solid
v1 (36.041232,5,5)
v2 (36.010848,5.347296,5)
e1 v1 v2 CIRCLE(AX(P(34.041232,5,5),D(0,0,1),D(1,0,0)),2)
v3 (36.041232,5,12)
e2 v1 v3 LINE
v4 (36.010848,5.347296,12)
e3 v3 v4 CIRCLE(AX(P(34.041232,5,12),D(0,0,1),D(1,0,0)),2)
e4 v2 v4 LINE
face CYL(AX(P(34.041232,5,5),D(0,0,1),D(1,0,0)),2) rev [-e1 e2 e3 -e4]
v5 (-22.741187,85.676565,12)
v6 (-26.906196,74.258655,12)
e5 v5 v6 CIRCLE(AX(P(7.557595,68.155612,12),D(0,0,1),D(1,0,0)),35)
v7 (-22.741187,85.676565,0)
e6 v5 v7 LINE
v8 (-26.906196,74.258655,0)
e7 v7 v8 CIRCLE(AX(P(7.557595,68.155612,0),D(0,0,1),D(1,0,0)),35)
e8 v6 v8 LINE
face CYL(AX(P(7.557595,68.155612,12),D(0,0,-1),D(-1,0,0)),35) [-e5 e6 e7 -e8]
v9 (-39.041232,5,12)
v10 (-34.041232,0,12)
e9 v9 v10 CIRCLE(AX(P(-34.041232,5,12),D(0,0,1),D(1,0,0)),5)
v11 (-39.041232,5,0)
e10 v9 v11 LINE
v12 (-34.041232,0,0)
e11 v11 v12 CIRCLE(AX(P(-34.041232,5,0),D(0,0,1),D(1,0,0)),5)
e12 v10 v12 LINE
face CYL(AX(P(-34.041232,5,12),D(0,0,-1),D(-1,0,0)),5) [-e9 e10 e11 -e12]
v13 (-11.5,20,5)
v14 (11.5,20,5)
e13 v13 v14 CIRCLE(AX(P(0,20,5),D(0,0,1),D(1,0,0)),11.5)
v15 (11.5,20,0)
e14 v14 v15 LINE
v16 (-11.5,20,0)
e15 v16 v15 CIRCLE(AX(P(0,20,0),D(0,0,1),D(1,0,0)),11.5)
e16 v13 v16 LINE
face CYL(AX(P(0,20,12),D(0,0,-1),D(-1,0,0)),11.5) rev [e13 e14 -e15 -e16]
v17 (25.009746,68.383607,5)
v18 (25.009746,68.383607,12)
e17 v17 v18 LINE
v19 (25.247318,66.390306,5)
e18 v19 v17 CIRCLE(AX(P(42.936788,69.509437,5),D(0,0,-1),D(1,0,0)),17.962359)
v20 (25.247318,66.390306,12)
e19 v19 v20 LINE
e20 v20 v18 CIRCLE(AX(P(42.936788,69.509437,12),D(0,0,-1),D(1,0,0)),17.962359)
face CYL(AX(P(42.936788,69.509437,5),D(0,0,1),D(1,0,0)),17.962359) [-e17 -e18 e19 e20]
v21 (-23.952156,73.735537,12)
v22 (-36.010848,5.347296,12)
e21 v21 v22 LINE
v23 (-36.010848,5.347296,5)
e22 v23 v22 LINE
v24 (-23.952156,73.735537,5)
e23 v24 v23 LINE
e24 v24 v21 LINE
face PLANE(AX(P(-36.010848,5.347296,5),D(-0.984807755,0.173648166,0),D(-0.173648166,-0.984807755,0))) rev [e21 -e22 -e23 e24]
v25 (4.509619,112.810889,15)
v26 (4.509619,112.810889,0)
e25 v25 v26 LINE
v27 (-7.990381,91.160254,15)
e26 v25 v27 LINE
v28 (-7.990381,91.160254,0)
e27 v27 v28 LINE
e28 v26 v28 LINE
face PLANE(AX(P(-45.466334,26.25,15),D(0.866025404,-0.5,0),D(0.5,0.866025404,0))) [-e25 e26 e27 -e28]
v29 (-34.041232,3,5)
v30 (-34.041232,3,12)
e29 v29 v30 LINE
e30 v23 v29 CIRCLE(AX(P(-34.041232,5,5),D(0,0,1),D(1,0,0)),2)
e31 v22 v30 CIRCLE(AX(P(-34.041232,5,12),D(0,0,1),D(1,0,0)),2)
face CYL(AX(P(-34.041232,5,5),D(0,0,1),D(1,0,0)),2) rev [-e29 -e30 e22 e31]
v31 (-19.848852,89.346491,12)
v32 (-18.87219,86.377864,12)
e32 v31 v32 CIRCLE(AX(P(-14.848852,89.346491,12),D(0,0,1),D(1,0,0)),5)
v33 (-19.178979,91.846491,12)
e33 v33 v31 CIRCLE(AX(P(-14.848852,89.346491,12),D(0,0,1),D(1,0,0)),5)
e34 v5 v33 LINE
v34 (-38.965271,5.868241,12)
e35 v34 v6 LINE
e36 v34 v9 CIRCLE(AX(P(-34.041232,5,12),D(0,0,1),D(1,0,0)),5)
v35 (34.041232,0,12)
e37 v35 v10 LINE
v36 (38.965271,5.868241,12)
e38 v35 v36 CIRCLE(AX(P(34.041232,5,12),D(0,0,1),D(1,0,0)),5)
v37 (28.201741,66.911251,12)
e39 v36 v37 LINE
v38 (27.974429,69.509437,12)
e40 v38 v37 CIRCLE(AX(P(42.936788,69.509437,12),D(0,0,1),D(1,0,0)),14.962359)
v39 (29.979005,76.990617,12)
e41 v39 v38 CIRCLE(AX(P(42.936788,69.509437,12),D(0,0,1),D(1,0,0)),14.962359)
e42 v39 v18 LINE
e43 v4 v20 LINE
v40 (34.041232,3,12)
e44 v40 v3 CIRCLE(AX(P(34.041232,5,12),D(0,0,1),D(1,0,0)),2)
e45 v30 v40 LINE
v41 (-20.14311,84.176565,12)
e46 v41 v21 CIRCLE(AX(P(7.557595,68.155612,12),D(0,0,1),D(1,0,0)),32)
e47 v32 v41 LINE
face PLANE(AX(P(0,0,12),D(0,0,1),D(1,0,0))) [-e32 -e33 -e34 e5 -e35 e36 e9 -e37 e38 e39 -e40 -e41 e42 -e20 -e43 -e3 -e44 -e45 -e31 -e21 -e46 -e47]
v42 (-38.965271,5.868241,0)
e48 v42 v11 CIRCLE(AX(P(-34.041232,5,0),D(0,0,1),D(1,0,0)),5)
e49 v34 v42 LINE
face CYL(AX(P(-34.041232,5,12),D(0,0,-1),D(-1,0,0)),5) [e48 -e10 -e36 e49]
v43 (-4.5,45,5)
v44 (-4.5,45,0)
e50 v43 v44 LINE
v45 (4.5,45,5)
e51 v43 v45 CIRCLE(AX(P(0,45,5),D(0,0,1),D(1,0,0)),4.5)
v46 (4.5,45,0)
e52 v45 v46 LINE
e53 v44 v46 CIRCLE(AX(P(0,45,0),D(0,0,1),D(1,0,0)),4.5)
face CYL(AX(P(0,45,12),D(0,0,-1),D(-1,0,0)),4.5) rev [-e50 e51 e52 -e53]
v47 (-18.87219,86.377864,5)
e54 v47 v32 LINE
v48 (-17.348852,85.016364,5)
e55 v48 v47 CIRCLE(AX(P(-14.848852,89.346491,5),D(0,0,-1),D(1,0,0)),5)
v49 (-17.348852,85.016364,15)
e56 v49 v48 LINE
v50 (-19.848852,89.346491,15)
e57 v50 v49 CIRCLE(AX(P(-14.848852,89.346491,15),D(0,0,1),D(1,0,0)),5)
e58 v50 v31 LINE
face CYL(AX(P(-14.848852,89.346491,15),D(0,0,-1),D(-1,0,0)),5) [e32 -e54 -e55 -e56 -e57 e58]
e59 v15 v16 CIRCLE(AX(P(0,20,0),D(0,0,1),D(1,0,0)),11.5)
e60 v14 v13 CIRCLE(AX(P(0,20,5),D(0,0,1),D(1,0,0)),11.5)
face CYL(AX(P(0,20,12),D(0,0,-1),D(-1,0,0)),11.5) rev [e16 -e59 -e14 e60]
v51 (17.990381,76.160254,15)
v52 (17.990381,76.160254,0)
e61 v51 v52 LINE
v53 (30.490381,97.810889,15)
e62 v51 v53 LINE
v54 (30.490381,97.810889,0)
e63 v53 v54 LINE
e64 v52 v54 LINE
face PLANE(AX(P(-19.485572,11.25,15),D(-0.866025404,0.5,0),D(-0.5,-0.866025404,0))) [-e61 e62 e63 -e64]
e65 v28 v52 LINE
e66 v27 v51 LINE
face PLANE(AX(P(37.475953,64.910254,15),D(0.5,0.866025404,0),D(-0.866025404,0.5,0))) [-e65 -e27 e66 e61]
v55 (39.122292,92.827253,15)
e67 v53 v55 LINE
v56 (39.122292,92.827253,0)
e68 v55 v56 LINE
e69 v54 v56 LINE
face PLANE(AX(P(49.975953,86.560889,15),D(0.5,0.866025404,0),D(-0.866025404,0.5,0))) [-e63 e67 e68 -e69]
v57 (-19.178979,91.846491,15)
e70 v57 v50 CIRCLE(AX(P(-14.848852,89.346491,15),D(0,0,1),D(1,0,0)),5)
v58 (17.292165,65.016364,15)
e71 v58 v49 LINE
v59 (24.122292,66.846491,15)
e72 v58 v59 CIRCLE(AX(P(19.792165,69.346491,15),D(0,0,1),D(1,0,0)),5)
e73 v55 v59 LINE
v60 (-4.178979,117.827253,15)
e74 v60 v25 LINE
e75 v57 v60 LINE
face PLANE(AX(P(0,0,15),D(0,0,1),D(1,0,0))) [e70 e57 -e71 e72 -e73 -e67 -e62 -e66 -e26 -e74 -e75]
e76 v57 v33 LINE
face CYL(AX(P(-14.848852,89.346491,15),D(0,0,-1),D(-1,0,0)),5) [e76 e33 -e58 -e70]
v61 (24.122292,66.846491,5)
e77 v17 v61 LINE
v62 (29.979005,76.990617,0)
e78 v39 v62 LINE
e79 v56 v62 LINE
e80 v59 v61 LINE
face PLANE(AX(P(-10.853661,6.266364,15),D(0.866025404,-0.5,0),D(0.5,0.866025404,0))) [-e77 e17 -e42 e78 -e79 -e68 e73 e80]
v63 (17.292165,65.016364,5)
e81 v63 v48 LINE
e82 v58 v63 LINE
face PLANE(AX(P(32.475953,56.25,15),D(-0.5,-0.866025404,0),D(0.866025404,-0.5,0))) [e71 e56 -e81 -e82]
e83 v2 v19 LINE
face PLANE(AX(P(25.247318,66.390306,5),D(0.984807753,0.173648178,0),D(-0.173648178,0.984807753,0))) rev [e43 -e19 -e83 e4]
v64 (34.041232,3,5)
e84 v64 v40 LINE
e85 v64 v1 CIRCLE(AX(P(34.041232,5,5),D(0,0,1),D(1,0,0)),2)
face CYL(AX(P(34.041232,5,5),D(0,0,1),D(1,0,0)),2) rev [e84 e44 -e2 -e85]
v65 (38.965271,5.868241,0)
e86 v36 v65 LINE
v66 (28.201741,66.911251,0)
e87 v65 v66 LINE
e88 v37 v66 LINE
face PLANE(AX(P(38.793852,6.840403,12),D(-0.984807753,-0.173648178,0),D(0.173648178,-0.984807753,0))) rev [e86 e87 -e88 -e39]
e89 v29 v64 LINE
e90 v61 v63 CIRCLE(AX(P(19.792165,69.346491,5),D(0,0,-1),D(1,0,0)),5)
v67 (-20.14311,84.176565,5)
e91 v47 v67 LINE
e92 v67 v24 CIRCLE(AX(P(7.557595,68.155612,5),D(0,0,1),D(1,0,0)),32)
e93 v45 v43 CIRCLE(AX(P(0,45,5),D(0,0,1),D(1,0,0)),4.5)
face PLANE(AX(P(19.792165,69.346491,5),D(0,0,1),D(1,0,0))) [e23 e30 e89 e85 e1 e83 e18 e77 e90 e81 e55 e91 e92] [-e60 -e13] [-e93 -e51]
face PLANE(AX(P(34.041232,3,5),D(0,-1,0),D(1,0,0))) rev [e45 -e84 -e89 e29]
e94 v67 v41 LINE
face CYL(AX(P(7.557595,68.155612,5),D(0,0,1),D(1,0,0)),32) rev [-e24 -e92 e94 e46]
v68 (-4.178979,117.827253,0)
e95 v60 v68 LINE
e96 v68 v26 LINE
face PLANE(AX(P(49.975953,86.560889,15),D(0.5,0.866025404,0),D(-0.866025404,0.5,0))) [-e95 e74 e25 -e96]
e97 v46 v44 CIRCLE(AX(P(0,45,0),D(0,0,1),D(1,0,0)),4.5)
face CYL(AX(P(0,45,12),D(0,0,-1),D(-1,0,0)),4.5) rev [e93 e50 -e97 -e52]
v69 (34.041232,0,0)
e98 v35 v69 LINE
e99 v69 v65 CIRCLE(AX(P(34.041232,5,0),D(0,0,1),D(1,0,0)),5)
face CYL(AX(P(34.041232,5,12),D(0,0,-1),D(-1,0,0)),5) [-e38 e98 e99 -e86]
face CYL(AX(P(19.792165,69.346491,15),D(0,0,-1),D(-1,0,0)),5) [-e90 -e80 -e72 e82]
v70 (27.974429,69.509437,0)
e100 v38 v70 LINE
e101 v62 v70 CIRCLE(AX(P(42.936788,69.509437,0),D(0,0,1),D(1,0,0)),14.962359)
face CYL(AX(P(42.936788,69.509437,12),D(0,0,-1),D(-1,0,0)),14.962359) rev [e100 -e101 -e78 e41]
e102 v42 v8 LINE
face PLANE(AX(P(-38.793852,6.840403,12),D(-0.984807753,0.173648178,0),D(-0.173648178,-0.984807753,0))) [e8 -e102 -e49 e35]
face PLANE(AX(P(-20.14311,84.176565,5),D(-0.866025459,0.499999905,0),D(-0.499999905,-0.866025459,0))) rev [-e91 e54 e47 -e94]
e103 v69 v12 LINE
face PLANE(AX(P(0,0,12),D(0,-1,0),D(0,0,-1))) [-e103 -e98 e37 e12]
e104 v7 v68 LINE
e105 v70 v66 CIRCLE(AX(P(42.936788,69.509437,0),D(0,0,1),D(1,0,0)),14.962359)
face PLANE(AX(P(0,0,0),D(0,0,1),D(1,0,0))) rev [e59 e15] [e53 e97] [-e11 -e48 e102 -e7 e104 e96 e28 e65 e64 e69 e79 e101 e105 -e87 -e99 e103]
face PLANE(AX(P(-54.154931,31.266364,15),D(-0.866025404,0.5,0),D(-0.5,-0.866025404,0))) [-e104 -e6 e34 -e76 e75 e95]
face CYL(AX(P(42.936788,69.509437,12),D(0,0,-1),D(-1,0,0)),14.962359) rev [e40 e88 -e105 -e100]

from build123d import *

# Parameters (mm, degrees)
FORK_BOSS_15MM_DEPTH           = 15
SKETCH1_10_R                   = 11.5
SKETCH1_10_R_2                 = 4.5
PLATE_BOSS_12MM_DEPTH          = 12
POCKET_START                   = -7
POCKET_AND_HOLES_CUT_7MM_DEPTH = 7


with BuildPart() as part:
    # Bracket Outline Sketch → Fork Boss 15mm (new body)
    with BuildSketch(Plane.XY):
        with BuildLine():
            Line((-17.348851567, 85.016364122), (17.292164585, 65.016364122))
            ThreePointArc((17.292164585, 65.016364122), (21.08625981, 64.51686201), (24.122291604, 66.846491141))
            Line((24.122291604, 66.846491141), (29.979005279, 76.990616791))
            Line((29.979005279, 76.990616791), (39.122291604, 92.827253255))
            Line((39.122291604, 92.827253255), (30.490381057, 97.810889132))
            Line((30.490381057, 97.810889132), (17.990381057, 76.160254038))
            Line((17.990381057, 76.160254038), (-7.990381057, 91.160254038))
            Line((-7.990381057, 91.160254038), (4.509618943, 112.810889132))
            Line((4.509618943, 112.810889132), (-4.178978585, 117.827253255))
            Line((-4.178978585, 117.827253255), (-19.178978585, 91.846491141))
            ThreePointArc((-19.178978585, 91.846491141), (-19.678480698, 88.052395915), (-17.348851567, 85.016364122))
        make_face()
    extrude(amount=FORK_BOSS_15MM_DEPTH)

    # Sketch1_10 → Plate Boss 12mm (add)
    with BuildSketch(Plane.XY):
        with BuildLine():
            ThreePointArc((24.122291604, 66.846491141), (21.08625981, 64.51686201), (17.292164585, 65.016364122))
            Line((17.292164585, 65.016364122), (-17.348851567, 85.016364122))
            ThreePointArc((-17.348851567, 85.016364122), (-19.678480698, 88.052395915), (-19.178978585, 91.846491141))
            Line((-19.178978585, 91.846491141), (-22.741186866, 85.676565412))
            ThreePointArc((-22.741186866, 85.676565412), (-25.323096431, 80.149782404), (-26.906195607, 74.258654802))
            Line((-26.906195607, 74.258654802), (-38.965270802, 5.868240888))
            ThreePointArc((-38.965270802, 5.868240888), (-37.871454253, 1.786061952), (-34.041232037, 0))
            Line((-34.041232037, 0), (34.041232037, 0))
            ThreePointArc((34.041232037, 0), (37.871454253, 1.786061952), (38.965270802, 5.868240888))
            Line((38.965270802, 5.868240888), (28.201741138, 66.911250985))
            ThreePointArc((28.201741138, 66.911250985), (28.201741138, 72.107623698), (29.979005279, 76.990616791))
            Line((29.979005279, 76.990616791), (24.122291604, 66.846491141))
        make_face()
        with Locations((0, 20)):
            Circle(SKETCH1_10_R, mode=Mode.SUBTRACT)
        with Locations((0, 45)):
            Circle(SKETCH1_10_R_2, mode=Mode.SUBTRACT)
    extrude(amount=PLATE_BOSS_12MM_DEPTH)

    # Pocket and Holes Sketch → Pocket and Holes Cut 7mm (cut)
    with BuildSketch(Plane.XY.offset(12).offset(POCKET_START)):
        with BuildLine():
            Line((25.009745942, 68.383607145), (24.122291604, 66.846491141))
            ThreePointArc((24.122291604, 66.846491141), (21.08625981, 64.51686201), (17.292164585, 65.016364122))
            Line((17.292164585, 65.016364122), (-17.348851567, 85.016364122))
            ThreePointArc((-17.348851567, 85.016364122), (-18.180803852, 85.618476392), (-18.872189895, 86.377863731))
            Line((-18.872189895, 86.377863731), (-20.143109976, 84.176565019))
            ThreePointArc((-20.143109976, 84.176565019), (-22.504396013, 79.122684974), (-23.952156408, 73.735536834))
            Line((-23.952156408, 73.735536834), (-36.010847543, 5.347296355))
            ThreePointArc((-36.010847543, 5.347296355), (-35.573320923, 3.714424781), (-34.041232037, 3))
            Line((-34.041232037, 3), (34.041232037, 3))
            ThreePointArc((34.041232037, 3), (35.573320923, 3.714424781), (36.010847543, 5.347296355))
            Line((36.010847543, 5.347296355), (25.247317879, 66.390306452))
            ThreePointArc((25.247317879, 66.390306452), (25.100664631, 67.383635431), (25.009745942, 68.383607145))
        make_face()
    extrude(amount=POCKET_AND_HOLES_CUT_7MM_DEPTH, mode=Mode.SUBTRACT)


solid = part.part
